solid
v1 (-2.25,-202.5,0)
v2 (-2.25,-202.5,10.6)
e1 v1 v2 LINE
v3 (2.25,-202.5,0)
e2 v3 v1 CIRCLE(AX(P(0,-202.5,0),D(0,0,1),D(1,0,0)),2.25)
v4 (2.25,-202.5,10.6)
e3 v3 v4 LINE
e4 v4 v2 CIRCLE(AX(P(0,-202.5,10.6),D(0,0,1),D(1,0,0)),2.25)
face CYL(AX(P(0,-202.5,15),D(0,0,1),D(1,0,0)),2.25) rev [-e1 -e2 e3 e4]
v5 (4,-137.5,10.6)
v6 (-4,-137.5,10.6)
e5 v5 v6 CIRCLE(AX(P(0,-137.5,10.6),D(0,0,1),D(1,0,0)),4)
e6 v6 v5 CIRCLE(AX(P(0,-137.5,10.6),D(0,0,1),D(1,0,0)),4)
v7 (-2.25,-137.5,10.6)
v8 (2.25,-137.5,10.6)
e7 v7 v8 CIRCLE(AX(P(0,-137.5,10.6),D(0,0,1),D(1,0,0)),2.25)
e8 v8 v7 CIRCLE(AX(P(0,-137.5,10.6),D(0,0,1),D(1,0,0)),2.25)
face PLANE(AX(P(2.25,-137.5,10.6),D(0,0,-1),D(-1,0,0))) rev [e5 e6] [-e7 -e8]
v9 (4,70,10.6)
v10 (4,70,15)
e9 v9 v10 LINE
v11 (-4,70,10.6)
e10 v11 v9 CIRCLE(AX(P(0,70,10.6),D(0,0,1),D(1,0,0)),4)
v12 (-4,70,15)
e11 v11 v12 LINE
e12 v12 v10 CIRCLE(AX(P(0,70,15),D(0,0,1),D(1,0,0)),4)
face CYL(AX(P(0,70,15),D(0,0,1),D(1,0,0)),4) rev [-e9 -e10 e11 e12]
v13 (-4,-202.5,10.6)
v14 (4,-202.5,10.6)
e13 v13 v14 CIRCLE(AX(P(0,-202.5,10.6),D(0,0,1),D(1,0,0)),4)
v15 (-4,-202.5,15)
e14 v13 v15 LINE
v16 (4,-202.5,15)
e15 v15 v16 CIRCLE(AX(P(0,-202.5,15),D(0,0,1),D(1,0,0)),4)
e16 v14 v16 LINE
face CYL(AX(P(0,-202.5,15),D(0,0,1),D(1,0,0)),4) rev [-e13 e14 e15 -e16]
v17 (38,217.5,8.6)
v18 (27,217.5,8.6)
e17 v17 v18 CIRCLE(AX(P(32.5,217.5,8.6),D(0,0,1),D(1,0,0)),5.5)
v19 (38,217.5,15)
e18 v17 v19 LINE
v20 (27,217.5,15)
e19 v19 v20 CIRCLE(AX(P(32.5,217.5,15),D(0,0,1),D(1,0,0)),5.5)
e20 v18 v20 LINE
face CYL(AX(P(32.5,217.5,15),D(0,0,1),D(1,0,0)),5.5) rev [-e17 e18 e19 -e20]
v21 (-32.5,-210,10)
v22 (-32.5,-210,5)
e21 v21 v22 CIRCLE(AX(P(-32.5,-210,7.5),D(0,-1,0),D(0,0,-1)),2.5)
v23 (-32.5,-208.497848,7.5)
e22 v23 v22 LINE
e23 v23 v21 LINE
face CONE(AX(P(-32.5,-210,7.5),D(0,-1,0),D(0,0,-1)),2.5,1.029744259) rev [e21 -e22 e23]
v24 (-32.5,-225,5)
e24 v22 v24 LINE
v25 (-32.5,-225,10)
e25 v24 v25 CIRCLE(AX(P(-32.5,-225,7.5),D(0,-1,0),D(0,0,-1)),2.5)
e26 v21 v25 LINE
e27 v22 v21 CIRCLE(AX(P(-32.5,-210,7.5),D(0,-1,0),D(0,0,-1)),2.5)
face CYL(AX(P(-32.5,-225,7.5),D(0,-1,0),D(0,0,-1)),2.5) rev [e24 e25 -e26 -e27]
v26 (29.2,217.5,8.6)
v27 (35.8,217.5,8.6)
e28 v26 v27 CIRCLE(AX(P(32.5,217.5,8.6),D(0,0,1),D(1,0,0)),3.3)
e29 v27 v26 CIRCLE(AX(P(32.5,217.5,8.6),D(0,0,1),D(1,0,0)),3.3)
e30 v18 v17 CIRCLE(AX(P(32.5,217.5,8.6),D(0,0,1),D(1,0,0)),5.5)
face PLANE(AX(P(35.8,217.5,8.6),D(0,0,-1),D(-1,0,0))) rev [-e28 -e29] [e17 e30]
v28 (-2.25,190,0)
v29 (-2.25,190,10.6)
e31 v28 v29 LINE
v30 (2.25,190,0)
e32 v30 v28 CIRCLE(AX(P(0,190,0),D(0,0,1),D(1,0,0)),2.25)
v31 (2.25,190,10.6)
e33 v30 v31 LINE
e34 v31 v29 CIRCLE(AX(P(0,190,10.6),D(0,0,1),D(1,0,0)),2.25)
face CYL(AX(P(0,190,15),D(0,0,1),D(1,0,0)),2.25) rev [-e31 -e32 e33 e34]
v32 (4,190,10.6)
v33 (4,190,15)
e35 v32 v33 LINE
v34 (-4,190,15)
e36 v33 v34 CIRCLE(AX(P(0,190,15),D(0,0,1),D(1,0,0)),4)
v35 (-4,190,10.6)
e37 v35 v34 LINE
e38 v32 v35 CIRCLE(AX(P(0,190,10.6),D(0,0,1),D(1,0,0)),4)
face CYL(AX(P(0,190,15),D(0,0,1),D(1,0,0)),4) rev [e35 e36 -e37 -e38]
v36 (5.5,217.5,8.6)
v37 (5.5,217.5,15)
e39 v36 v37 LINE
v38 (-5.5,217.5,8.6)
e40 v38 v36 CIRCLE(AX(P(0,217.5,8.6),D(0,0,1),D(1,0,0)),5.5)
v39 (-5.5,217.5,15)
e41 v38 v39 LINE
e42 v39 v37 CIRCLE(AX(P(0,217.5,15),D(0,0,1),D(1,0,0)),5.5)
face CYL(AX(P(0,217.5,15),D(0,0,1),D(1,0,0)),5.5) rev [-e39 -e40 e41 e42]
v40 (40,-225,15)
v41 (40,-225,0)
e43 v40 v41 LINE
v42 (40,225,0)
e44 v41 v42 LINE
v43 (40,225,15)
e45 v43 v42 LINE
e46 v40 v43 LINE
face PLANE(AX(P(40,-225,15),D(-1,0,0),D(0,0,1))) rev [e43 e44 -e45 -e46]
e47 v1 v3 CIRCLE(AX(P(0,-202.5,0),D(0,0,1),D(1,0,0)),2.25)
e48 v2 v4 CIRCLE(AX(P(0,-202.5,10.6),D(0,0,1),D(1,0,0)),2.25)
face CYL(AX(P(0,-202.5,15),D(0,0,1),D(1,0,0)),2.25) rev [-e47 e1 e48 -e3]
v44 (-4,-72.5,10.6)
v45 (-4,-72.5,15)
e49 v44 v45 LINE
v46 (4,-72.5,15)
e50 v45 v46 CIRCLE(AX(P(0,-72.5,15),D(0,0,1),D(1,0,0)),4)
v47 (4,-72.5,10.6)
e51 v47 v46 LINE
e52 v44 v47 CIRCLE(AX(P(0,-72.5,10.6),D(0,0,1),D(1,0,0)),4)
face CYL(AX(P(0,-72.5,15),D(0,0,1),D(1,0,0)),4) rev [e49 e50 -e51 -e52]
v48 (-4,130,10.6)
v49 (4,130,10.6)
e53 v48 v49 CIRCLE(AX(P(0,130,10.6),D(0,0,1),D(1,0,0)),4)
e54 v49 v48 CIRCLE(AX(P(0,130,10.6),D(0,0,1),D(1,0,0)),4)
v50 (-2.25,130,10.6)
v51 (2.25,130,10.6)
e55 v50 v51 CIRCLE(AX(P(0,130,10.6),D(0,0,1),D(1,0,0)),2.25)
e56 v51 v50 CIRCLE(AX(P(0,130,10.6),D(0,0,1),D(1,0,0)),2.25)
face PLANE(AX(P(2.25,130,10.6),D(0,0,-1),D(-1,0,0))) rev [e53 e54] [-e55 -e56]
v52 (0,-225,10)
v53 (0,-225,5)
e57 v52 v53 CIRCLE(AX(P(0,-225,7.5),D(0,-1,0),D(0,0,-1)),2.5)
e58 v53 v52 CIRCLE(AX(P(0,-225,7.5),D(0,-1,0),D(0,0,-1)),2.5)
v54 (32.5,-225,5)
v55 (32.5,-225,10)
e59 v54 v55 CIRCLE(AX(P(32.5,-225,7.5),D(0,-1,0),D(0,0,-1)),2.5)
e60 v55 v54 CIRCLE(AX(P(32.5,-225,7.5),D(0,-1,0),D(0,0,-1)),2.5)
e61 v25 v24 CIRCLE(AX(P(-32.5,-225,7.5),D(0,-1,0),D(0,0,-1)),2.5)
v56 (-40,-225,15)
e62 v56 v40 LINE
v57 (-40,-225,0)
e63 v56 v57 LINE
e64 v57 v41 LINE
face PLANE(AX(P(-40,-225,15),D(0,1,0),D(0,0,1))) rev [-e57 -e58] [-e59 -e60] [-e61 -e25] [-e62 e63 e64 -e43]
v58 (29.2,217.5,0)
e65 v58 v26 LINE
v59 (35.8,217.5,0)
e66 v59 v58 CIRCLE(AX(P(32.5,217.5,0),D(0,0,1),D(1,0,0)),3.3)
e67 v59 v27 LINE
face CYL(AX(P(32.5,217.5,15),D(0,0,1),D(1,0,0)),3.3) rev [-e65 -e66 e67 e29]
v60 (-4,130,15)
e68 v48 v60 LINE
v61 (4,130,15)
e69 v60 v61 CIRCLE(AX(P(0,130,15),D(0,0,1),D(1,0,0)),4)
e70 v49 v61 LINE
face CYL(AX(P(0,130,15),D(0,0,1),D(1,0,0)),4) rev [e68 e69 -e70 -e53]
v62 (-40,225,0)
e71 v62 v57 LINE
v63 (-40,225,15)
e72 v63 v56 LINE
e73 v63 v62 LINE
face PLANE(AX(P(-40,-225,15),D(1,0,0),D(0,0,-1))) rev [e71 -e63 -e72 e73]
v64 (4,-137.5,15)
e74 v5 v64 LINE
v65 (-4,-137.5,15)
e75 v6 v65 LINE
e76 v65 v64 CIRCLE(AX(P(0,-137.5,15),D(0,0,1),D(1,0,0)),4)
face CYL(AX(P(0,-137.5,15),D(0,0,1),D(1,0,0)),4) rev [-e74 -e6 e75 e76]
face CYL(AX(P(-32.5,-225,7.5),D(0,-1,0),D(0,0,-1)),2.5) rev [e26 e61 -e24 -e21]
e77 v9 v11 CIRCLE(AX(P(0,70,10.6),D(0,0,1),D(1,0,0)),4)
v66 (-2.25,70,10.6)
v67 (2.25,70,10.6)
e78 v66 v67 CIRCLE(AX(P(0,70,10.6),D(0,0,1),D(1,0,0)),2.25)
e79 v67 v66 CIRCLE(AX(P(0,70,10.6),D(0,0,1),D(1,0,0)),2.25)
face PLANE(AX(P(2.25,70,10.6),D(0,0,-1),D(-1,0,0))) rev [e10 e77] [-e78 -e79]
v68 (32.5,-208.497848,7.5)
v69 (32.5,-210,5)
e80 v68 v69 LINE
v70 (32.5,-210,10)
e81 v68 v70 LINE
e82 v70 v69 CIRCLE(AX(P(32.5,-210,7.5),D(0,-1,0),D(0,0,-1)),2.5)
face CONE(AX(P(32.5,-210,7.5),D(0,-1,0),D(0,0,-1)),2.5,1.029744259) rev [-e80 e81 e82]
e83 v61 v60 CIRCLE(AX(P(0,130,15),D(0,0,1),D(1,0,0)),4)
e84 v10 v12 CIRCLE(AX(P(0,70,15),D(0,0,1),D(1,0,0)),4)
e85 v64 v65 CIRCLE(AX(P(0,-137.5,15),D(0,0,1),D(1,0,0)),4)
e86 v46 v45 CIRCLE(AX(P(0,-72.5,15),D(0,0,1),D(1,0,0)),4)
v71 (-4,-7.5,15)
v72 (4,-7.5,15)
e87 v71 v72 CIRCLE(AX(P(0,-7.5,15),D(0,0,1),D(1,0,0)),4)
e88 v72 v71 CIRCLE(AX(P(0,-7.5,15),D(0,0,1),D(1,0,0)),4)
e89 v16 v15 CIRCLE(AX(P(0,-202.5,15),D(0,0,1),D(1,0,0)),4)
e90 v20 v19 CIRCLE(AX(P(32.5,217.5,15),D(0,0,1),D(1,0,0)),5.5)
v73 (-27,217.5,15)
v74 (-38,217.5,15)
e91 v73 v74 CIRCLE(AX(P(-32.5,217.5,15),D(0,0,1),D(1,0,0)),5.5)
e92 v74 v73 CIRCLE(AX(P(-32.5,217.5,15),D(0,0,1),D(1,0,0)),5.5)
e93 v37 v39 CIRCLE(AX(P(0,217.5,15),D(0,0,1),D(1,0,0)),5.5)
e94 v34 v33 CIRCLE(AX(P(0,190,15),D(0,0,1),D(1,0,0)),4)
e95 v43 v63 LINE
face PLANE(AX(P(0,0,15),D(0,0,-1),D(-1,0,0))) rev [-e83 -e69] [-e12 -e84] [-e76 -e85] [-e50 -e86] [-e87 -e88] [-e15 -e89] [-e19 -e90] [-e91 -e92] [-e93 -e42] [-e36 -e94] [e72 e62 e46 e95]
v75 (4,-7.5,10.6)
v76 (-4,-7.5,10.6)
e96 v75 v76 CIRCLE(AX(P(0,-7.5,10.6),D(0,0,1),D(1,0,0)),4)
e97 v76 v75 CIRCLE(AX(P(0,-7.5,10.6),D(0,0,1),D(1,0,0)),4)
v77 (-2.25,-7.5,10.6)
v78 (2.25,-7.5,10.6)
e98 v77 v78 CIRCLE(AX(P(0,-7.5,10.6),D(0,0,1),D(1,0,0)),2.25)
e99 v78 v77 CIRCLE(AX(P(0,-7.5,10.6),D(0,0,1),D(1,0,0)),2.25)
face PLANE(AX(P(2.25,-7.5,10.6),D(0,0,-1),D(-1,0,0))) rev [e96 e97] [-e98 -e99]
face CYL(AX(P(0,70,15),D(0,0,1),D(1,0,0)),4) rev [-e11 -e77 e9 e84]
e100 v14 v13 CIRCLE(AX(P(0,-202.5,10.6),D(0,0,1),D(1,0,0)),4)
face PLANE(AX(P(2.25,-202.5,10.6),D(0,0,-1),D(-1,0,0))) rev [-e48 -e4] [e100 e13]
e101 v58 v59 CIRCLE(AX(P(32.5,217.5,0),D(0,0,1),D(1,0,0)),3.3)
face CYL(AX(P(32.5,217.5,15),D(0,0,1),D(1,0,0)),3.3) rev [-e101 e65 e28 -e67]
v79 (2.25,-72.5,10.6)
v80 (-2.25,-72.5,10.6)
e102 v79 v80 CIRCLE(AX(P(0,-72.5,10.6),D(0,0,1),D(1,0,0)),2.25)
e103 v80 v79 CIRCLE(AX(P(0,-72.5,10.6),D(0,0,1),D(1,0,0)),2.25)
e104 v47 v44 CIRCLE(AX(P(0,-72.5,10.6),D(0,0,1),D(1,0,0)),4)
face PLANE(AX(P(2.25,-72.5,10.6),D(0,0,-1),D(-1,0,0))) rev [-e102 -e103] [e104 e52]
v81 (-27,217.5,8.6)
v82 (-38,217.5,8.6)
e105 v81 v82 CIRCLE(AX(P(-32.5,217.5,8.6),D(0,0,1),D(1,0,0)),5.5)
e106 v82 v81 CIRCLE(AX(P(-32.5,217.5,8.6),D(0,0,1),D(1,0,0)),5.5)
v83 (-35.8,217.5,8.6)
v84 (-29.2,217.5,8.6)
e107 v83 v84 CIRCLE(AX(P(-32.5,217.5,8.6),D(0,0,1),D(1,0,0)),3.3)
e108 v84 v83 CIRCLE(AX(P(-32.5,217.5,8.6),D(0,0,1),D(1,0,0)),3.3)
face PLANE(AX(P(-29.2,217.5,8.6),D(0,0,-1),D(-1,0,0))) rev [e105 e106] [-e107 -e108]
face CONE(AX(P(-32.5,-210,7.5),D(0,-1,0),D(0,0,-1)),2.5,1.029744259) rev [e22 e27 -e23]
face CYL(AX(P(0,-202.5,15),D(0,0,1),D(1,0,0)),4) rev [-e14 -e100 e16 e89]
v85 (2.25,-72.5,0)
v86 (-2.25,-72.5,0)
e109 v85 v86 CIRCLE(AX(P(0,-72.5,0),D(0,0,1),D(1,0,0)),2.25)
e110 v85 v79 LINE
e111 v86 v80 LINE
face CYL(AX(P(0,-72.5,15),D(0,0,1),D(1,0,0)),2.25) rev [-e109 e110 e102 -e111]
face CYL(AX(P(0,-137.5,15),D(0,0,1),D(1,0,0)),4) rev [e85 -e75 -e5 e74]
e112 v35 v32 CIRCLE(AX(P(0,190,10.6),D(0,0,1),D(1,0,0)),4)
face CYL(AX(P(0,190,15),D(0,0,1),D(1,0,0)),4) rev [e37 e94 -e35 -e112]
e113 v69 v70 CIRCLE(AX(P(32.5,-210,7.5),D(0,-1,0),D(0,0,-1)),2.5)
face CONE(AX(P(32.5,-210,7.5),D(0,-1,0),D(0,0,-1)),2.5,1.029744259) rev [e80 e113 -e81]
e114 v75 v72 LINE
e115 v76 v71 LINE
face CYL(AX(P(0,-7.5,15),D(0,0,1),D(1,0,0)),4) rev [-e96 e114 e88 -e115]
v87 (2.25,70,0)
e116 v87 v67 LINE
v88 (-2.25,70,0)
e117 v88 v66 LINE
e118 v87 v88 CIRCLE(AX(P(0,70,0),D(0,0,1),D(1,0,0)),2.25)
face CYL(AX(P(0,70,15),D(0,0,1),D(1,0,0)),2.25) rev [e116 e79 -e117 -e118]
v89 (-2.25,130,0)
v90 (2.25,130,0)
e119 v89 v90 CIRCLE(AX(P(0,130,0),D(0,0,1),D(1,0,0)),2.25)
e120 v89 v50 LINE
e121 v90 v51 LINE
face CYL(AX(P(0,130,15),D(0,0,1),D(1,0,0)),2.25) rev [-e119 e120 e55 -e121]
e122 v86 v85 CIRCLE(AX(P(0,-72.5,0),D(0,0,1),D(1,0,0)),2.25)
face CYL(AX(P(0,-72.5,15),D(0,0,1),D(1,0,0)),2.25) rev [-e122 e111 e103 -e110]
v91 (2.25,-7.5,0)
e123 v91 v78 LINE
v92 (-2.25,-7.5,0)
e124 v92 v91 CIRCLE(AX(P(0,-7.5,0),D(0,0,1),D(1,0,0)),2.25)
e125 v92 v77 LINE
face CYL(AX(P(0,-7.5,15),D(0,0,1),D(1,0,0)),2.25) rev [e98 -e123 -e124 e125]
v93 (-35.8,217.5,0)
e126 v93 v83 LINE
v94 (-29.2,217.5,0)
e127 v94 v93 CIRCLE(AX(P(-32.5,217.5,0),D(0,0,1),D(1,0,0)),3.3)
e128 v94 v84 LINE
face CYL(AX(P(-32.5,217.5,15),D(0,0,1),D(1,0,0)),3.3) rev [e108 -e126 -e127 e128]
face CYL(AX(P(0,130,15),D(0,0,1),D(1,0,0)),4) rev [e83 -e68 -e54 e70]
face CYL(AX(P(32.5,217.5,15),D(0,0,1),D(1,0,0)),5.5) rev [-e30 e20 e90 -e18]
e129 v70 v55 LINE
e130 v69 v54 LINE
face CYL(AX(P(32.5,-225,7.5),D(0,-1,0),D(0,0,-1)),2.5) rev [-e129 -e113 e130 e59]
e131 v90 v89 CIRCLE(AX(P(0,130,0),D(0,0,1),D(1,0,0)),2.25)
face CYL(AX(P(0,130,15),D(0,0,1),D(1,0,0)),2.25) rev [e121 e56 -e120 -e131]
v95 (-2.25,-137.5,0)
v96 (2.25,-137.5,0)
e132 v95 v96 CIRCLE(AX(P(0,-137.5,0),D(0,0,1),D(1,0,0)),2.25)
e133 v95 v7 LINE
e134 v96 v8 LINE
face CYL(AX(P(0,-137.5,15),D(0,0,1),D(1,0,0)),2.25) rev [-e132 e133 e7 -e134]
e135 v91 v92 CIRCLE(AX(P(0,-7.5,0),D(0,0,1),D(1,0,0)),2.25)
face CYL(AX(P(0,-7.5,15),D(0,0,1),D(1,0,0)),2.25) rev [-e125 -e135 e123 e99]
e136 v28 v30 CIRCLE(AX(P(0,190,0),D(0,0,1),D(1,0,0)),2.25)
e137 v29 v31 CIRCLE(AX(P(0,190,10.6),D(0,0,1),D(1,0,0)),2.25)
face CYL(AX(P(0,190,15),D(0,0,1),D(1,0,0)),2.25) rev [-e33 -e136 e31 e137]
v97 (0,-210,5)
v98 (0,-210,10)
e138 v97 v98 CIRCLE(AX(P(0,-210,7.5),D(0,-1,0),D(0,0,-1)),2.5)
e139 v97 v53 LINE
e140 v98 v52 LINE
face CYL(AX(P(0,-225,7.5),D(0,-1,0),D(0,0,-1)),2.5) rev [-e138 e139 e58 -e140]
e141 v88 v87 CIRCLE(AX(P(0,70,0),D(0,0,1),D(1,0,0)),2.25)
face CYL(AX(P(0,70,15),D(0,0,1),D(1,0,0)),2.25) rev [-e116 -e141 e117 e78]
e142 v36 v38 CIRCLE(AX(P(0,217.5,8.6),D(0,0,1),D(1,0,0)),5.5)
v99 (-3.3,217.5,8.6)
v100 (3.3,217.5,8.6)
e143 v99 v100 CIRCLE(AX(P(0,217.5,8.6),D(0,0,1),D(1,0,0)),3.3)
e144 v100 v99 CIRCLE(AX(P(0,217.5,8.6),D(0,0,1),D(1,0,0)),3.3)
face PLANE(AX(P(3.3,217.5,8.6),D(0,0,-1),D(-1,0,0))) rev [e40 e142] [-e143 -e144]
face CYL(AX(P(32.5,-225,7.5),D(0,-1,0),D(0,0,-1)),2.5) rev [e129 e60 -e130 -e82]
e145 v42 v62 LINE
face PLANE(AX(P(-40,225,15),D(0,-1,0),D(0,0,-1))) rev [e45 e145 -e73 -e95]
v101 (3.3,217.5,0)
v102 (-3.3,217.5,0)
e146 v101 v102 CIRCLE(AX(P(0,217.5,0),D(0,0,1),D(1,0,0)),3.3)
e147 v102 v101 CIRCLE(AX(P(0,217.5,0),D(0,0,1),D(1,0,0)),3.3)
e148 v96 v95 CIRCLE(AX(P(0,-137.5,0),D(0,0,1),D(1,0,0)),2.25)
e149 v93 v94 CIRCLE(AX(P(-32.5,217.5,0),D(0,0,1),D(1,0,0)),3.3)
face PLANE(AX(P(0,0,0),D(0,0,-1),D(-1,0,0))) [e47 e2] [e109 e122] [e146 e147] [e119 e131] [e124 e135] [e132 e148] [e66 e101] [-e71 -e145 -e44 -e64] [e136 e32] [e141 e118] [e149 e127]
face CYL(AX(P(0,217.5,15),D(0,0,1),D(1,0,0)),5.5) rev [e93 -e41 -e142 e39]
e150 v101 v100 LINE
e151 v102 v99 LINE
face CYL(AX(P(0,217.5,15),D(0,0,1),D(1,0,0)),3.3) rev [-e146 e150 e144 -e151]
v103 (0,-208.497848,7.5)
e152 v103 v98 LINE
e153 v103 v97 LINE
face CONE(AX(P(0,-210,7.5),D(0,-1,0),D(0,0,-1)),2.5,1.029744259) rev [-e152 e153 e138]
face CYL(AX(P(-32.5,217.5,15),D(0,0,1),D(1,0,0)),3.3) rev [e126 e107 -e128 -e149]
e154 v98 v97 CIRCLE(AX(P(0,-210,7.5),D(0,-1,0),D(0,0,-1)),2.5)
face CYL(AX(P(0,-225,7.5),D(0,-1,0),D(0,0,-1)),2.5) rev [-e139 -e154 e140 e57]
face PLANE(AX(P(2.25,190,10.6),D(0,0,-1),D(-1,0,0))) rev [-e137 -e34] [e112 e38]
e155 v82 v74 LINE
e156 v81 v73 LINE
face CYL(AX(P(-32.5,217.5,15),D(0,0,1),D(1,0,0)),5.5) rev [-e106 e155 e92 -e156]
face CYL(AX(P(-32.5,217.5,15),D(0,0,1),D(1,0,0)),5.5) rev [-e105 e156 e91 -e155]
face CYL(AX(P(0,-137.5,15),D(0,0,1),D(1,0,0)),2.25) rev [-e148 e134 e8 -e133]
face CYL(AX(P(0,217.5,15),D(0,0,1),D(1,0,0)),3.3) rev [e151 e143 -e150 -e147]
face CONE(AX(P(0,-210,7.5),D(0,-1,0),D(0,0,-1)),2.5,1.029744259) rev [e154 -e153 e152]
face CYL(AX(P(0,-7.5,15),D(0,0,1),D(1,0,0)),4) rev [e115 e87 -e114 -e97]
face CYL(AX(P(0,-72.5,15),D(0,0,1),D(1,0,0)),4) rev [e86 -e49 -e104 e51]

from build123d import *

# Parameters (mm, degrees)
SKETCH_1_W                   = 80
SKETCH_1_H                   = 450
EXTRUDE_1_DEPTH              = 15
HOLE_WIZARD_M6_1_D           = 6.6
HOLE_WIZARD_M6_1_CBORE_D     = 11
HOLE_WIZARD_M6_1_CBORE_DEPTH = 6.4
HOLE_WIZARD_M4_1_D           = 4.5
HOLE_WIZARD_M4_1_CBORE_D     = 8
HOLE_WIZARD_M4_1_CBORE_DEPTH = 4.4
HOLE_WIZARD_M4_2_D           = 4.5
HOLE_WIZARD_M4_2_CBORE_D     = 8
HOLE_WIZARD_M4_2_CBORE_DEPTH = 4.4
HOLE_WIZARD_M6_1_2_D         = 5
HOLE_WIZARD_M6_1_2_DEPTH     = 15
HOLE_WIZARD_M6_1_2_TIP       = 1.502151548


with BuildPart() as part:
    # 草图1 → 凸台-拉伸1 (new body)
    with BuildSketch(Plane.XY):
        Rectangle(SKETCH_1_W, SKETCH_1_H)
    extrude(amount=EXTRUDE_1_DEPTH)

    # Hole Wizard M6 _1 (through all)
    with Locations(Plane.XY.offset(15)):
        with Locations((-32.5, 217.5), (32.5, 217.5), (0, 217.5)):
            CounterBoreHole(HOLE_WIZARD_M6_1_D / 2, HOLE_WIZARD_M6_1_CBORE_D / 2, HOLE_WIZARD_M6_1_CBORE_DEPTH)

    # M4 六角凹头螺钉的柱形沉头孔1 (through all)
    with Locations(Plane.XY.offset(15)):
        with Locations((0, 190), (0, 130), (0, 70)):
            CounterBoreHole(HOLE_WIZARD_M4_1_D / 2, HOLE_WIZARD_M4_1_CBORE_D / 2, HOLE_WIZARD_M4_1_CBORE_DEPTH)

    # M4 六角凹头螺钉的柱形沉头孔2 (through all)
    with Locations(Plane.XY.offset(15)):
        with Locations((0, -202.5), (0, -137.5), (0, -72.5), (0, -7.5)):
            CounterBoreHole(HOLE_WIZARD_M4_2_D / 2, HOLE_WIZARD_M4_2_CBORE_D / 2, HOLE_WIZARD_M4_2_CBORE_DEPTH)

    # Hole Wizard M6 _1 2
    with Locations(Plane(origin=(0, -225, 0), x_dir=(-1, 0, 0), z_dir=(0, -1, 0))):
        with Locations((32.5, -7.5), (0, -7.5), (-32.5, -7.5)):
            Hole(HOLE_WIZARD_M6_1_2_D / 2, depth=HOLE_WIZARD_M6_1_2_DEPTH)
            with Locations((0, 0, -(HOLE_WIZARD_M6_1_2_DEPTH + HOLE_WIZARD_M6_1_2_TIP / 2))):  # 118° drill point
                Cone(0, HOLE_WIZARD_M6_1_2_D / 2, HOLE_WIZARD_M6_1_2_TIP, mode=Mode.SUBTRACT)


solid = part.part
